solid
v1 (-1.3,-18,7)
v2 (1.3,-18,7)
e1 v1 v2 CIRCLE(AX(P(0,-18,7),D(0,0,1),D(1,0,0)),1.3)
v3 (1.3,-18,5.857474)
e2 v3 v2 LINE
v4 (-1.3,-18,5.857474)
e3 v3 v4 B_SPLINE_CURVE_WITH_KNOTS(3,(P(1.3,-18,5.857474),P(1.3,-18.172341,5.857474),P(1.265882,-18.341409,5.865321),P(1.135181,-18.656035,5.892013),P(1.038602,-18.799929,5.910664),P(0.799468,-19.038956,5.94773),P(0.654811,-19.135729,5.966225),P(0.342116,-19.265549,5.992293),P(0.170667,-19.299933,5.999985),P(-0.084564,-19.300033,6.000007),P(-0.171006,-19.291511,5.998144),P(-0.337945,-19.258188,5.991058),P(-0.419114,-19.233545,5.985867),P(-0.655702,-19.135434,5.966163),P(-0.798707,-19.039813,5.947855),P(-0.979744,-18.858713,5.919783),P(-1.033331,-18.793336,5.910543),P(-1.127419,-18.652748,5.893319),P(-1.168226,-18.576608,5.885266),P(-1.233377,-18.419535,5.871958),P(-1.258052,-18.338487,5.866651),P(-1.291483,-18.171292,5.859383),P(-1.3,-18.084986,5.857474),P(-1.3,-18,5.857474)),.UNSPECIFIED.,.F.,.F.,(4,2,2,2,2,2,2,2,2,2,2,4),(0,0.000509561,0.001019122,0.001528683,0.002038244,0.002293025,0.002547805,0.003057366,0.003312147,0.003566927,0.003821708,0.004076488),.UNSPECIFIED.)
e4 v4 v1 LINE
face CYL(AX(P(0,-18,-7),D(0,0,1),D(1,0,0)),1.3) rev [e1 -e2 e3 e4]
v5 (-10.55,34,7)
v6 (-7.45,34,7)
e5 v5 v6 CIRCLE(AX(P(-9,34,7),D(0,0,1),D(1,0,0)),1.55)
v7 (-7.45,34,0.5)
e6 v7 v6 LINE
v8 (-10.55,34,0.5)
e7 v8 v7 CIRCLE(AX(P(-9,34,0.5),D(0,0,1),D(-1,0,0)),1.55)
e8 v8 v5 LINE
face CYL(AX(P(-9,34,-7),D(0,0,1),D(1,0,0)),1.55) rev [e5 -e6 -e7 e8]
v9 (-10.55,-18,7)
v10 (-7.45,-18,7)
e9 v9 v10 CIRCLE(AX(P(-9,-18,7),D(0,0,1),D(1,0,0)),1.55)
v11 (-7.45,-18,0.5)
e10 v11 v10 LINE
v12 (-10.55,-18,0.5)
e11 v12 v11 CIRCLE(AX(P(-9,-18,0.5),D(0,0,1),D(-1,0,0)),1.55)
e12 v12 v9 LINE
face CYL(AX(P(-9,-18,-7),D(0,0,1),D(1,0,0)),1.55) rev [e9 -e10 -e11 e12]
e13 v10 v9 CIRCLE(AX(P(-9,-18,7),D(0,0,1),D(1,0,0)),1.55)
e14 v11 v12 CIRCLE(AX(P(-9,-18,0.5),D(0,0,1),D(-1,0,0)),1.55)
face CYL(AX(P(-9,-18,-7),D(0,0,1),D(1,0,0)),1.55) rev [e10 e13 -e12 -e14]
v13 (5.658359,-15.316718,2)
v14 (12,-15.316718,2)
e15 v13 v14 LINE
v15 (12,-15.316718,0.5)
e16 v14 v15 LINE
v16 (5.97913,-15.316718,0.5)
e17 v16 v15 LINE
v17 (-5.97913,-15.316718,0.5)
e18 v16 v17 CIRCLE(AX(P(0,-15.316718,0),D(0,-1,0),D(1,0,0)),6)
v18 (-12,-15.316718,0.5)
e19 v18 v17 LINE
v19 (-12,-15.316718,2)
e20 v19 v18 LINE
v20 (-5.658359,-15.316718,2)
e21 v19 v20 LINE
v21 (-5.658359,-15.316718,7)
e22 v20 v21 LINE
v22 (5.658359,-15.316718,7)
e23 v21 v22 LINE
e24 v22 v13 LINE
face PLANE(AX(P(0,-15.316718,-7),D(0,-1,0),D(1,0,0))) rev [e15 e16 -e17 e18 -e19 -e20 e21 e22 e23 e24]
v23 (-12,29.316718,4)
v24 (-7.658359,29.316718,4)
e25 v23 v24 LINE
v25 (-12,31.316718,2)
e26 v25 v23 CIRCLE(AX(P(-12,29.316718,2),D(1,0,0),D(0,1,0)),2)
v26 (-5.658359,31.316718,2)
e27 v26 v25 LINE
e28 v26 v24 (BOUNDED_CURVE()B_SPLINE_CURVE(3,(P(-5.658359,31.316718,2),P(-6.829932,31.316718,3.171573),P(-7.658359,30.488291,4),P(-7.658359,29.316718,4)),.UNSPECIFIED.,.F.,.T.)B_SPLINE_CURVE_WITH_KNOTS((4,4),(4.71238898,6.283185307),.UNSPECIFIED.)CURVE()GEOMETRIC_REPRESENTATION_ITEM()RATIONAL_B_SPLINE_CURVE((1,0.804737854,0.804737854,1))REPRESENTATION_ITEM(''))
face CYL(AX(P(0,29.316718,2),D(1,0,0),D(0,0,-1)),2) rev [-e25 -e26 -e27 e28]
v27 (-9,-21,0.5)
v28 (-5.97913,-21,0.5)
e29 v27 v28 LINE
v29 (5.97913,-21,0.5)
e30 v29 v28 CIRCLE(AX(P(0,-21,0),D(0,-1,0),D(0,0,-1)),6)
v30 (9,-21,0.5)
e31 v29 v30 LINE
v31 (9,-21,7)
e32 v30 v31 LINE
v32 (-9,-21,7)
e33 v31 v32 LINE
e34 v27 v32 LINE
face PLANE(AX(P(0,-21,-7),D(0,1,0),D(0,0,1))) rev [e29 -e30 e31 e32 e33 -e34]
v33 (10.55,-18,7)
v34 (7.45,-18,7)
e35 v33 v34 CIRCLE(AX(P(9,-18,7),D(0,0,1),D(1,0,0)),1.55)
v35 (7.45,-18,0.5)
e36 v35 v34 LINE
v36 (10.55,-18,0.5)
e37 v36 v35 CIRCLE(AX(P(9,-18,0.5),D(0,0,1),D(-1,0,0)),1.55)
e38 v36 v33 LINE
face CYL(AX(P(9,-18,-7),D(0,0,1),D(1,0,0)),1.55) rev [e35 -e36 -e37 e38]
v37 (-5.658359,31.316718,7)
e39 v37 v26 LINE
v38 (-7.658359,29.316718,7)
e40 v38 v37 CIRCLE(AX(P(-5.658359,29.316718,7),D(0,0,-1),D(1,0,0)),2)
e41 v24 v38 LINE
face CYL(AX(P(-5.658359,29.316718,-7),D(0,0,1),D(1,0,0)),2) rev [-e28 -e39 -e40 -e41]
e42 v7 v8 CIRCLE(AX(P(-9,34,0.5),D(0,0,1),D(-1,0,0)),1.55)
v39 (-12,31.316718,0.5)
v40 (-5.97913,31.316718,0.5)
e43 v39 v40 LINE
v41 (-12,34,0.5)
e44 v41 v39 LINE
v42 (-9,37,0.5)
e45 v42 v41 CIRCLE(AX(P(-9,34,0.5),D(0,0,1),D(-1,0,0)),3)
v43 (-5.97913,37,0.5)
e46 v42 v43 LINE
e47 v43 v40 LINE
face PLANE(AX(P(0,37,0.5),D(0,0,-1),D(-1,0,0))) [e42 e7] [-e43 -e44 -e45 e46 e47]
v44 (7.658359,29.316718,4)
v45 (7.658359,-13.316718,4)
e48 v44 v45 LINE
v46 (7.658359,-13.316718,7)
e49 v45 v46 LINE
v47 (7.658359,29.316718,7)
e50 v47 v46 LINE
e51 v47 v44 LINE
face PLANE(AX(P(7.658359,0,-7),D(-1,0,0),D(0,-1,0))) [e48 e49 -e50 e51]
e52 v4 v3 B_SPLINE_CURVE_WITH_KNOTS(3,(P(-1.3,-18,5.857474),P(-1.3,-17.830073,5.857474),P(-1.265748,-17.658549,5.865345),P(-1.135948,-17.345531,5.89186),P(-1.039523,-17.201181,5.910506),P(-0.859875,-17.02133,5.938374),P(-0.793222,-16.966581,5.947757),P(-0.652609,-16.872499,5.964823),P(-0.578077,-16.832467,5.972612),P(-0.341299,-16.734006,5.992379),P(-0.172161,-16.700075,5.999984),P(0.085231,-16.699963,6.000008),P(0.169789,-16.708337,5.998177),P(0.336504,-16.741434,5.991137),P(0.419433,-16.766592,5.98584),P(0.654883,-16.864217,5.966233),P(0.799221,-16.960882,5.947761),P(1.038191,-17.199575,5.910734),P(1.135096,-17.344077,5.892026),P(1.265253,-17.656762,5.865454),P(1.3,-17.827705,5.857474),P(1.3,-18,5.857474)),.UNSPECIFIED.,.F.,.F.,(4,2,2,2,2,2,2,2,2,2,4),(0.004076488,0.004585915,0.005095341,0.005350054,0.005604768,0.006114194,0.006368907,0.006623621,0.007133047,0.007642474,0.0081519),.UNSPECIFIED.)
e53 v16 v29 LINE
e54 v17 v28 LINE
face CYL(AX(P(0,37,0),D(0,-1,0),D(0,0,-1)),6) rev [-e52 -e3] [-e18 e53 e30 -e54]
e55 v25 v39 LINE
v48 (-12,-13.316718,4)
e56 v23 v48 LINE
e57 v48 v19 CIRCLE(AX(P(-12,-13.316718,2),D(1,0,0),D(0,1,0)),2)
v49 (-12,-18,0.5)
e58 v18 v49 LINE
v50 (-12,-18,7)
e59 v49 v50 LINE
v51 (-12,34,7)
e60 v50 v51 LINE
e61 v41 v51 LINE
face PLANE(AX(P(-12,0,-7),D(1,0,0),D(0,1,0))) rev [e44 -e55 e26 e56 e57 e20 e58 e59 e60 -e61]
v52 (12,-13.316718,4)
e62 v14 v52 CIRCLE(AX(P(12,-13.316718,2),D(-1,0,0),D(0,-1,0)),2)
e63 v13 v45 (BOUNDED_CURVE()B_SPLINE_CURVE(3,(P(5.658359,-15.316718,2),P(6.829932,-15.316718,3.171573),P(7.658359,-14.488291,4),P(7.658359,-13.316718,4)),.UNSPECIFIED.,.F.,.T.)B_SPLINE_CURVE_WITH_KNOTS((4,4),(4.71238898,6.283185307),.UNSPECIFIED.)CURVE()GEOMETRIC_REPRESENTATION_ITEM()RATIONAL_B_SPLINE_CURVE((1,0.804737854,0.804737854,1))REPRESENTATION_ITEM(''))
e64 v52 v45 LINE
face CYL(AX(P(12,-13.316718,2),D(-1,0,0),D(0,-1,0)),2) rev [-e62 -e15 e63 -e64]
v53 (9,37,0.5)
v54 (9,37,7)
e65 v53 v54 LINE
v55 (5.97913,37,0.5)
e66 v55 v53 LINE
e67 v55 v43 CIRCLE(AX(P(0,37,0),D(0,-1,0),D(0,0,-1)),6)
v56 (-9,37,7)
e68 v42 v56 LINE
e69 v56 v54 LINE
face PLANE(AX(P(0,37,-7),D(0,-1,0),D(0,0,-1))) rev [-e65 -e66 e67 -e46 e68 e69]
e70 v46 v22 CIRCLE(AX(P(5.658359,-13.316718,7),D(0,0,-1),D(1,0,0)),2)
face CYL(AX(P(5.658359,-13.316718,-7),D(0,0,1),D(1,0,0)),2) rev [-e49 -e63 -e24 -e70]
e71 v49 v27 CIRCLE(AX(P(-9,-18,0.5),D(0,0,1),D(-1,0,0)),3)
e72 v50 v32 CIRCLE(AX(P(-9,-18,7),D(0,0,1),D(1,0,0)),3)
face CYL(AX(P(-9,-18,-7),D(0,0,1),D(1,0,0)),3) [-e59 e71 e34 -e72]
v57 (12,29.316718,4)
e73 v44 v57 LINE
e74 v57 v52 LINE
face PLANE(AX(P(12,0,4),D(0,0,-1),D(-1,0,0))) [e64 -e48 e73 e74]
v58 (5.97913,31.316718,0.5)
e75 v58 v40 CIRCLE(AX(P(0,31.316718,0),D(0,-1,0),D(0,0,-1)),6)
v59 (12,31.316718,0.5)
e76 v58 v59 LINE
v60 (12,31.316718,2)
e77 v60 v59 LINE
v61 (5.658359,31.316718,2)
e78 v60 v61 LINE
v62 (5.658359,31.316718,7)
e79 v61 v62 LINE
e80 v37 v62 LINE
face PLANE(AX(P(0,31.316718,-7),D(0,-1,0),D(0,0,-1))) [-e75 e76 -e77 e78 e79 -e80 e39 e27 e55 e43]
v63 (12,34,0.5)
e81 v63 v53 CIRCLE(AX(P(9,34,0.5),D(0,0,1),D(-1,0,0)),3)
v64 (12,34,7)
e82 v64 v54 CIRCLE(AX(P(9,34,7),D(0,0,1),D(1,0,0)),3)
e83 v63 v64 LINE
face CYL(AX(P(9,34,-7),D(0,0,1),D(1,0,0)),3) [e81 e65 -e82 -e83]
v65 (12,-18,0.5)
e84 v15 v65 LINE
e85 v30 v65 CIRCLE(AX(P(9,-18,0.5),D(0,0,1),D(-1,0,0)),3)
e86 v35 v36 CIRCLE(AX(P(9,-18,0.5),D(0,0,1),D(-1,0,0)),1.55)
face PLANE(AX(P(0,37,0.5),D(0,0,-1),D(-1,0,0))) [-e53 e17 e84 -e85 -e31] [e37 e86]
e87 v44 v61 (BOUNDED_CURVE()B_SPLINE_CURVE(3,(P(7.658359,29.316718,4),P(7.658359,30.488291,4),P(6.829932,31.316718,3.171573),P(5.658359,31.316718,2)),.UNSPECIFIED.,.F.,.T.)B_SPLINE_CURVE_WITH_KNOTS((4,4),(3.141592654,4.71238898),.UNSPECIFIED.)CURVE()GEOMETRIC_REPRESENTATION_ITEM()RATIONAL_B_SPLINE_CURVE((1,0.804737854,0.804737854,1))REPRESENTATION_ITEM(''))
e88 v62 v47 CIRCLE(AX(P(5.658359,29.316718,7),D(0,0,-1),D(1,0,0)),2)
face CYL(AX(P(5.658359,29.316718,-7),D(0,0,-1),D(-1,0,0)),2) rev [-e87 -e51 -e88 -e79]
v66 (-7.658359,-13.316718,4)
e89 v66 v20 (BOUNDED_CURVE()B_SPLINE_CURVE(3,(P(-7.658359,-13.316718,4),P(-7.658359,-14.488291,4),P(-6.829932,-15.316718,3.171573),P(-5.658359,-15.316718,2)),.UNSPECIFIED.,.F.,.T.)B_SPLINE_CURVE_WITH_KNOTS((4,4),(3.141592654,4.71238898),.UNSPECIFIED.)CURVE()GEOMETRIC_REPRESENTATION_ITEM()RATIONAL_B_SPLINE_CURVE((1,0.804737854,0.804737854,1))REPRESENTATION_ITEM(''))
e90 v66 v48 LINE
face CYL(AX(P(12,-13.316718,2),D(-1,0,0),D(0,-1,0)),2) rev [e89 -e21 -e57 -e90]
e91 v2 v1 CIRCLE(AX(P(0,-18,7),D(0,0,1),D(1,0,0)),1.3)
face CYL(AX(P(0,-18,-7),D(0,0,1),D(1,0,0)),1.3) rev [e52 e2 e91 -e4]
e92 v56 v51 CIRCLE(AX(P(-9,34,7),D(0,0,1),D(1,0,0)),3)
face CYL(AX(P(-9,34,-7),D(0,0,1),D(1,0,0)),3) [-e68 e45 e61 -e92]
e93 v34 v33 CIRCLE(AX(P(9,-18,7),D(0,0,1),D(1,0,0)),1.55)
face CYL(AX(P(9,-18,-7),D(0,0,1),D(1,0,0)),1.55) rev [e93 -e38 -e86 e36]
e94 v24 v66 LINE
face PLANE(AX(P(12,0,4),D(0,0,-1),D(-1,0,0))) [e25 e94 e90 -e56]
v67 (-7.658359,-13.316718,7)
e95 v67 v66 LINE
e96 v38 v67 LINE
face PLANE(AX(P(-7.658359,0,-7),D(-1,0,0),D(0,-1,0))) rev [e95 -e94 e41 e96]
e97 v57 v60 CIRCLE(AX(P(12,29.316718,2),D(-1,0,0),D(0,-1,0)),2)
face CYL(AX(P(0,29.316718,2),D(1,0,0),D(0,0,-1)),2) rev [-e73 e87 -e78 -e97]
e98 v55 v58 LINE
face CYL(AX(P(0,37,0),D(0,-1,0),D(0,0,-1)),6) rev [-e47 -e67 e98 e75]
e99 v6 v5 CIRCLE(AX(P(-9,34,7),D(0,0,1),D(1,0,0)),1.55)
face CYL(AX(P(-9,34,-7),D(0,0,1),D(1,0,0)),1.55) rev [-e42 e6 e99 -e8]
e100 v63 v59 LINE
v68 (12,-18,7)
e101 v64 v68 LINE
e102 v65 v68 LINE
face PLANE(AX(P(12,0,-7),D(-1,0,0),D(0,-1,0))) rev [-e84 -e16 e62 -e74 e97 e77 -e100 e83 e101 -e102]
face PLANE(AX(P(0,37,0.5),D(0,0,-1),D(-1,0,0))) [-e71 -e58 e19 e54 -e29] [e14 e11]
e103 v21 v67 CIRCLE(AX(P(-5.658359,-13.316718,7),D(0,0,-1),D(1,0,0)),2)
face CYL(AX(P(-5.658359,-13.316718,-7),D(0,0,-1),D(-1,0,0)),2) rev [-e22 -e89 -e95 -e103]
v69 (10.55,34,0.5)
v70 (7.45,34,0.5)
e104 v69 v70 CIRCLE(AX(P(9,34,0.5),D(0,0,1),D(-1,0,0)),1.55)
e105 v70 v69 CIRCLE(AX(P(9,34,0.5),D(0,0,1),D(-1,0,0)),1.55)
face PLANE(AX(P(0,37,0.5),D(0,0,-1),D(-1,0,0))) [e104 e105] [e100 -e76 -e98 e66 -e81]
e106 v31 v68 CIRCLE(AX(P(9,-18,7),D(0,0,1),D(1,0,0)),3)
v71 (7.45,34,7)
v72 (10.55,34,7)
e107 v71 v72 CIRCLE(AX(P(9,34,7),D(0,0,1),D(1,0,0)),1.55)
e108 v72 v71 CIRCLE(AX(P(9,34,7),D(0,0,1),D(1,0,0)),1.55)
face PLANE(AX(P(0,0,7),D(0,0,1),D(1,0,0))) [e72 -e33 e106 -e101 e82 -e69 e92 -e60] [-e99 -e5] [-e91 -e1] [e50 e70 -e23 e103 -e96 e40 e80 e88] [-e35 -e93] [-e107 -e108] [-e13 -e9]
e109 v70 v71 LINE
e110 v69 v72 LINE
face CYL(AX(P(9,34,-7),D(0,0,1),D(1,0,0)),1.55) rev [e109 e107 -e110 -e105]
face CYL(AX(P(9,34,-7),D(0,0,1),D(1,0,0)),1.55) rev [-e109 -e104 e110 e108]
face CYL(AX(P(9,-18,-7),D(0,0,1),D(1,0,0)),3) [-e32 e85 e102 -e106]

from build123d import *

# Parameters (mm, degrees)
EXTRUDE_1_DEPTH      = 7
EXTRUDE_1_DEPTH_BACK = 7
SKETCH_2_R           = 1.55
SKETCH_2_R_2         = 1.3
SKETCH_2_W           = 15.316718428
SKETCH_2_H           = 46.633436854
CUT_EXTRUDE_1_DEPTH  = 60.640590205
SKETCH_4_W           = 3.5
SKETCH_4_H           = 46.633436854
CUT_EXTRUDE_2_DEPTH  = 45.654227139
FILLET_1_R           = 2


with BuildPart() as part:
    # 草图2 → 凸台-拉伸1 (new, two sides: drawn at the far end of the back side and taken through both)
    with BuildSketch(Plane.XY.offset(-EXTRUDE_1_DEPTH_BACK)):
        with BuildLine():
            Line((9, 37), (-9, 37))
            ThreePointArc((-9, 37), (-11.121320344, 36.121320344), (-12, 34))
            Line((-12, 34), (-12, -18))
            ThreePointArc((-12, -18), (-11.121320344, -20.121320344), (-9, -21))
            Line((-9, -21), (9, -21))
            ThreePointArc((9, -21), (11.121320344, -20.121320344), (12, -18))
            Line((12, -18), (12, 34))
            ThreePointArc((12, 34), (11.121320344, 36.121320344), (9, 37))
        make_face()
        with Locations((-9, -18)):
            Circle(SKETCH_2_R, mode=Mode.SUBTRACT)
        with Locations((0, -18)):
            Circle(SKETCH_2_R_2, mode=Mode.SUBTRACT)
        with Locations((9, -18)):
            Circle(SKETCH_2_R, mode=Mode.SUBTRACT)
        with Locations((0, 8)):
            Rectangle(SKETCH_2_W, SKETCH_2_H, mode=Mode.SUBTRACT)
        with Locations((9, 34)):
            Circle(SKETCH_2_R, mode=Mode.SUBTRACT)
        with Locations((-9, 34)):
            Circle(SKETCH_2_R, mode=Mode.SUBTRACT)
    extrude(amount=EXTRUDE_1_DEPTH + EXTRUDE_1_DEPTH_BACK)

    # 草图3 → 切除-拉伸1 (cut, through all)
    with BuildSketch(Plane.XZ.offset(21)):
        with BuildLine():
            Line((-12, 0.5), (-5.979130372, 0.5))
            ThreePointArc((-5.979130372, 0.5), (0, 6), (5.979130372, 0.5))
            Line((5.979130372, 0.5), (12, 0.5))
            Line((12, 0.5), (12, -7))
            Line((12, -7), (-12, -7))
            Line((-12, -7), (-12, 0.5))
        make_face()
    extrude(amount=-CUT_EXTRUDE_1_DEPTH, mode=Mode.SUBTRACT)

    # 草图4 → 切除-拉伸2 (cut, through all)
    with BuildSketch(Plane.ZY.offset(12)):
        with Locations((2.25, 8)):
            Rectangle(SKETCH_4_W, SKETCH_4_H)
    extrude(amount=-CUT_EXTRUDE_2_DEPTH, mode=Mode.SUBTRACT)

    # 圆角1
    fillet_1_edges = [part.edges().sort_by_distance(p)[0] for p in [
        (7.658359214, 31.316718427, 5.5),
        (-7.658359214, 31.316718427, 5.5),
        (7.658359214, -15.316718427, 5.5),
        (-7.658359214, -15.316718427, 5.5),
        (-9.829179607, 31.316718427, 4),
        (-9.829179607, -15.316718427, 4),
        (9.829179607, -15.316718427, 4),
        (9.829179607, 31.316718427, 4),
    ]]
    fillet(fillet_1_edges, radius=FILLET_1_R)


solid = part.part
